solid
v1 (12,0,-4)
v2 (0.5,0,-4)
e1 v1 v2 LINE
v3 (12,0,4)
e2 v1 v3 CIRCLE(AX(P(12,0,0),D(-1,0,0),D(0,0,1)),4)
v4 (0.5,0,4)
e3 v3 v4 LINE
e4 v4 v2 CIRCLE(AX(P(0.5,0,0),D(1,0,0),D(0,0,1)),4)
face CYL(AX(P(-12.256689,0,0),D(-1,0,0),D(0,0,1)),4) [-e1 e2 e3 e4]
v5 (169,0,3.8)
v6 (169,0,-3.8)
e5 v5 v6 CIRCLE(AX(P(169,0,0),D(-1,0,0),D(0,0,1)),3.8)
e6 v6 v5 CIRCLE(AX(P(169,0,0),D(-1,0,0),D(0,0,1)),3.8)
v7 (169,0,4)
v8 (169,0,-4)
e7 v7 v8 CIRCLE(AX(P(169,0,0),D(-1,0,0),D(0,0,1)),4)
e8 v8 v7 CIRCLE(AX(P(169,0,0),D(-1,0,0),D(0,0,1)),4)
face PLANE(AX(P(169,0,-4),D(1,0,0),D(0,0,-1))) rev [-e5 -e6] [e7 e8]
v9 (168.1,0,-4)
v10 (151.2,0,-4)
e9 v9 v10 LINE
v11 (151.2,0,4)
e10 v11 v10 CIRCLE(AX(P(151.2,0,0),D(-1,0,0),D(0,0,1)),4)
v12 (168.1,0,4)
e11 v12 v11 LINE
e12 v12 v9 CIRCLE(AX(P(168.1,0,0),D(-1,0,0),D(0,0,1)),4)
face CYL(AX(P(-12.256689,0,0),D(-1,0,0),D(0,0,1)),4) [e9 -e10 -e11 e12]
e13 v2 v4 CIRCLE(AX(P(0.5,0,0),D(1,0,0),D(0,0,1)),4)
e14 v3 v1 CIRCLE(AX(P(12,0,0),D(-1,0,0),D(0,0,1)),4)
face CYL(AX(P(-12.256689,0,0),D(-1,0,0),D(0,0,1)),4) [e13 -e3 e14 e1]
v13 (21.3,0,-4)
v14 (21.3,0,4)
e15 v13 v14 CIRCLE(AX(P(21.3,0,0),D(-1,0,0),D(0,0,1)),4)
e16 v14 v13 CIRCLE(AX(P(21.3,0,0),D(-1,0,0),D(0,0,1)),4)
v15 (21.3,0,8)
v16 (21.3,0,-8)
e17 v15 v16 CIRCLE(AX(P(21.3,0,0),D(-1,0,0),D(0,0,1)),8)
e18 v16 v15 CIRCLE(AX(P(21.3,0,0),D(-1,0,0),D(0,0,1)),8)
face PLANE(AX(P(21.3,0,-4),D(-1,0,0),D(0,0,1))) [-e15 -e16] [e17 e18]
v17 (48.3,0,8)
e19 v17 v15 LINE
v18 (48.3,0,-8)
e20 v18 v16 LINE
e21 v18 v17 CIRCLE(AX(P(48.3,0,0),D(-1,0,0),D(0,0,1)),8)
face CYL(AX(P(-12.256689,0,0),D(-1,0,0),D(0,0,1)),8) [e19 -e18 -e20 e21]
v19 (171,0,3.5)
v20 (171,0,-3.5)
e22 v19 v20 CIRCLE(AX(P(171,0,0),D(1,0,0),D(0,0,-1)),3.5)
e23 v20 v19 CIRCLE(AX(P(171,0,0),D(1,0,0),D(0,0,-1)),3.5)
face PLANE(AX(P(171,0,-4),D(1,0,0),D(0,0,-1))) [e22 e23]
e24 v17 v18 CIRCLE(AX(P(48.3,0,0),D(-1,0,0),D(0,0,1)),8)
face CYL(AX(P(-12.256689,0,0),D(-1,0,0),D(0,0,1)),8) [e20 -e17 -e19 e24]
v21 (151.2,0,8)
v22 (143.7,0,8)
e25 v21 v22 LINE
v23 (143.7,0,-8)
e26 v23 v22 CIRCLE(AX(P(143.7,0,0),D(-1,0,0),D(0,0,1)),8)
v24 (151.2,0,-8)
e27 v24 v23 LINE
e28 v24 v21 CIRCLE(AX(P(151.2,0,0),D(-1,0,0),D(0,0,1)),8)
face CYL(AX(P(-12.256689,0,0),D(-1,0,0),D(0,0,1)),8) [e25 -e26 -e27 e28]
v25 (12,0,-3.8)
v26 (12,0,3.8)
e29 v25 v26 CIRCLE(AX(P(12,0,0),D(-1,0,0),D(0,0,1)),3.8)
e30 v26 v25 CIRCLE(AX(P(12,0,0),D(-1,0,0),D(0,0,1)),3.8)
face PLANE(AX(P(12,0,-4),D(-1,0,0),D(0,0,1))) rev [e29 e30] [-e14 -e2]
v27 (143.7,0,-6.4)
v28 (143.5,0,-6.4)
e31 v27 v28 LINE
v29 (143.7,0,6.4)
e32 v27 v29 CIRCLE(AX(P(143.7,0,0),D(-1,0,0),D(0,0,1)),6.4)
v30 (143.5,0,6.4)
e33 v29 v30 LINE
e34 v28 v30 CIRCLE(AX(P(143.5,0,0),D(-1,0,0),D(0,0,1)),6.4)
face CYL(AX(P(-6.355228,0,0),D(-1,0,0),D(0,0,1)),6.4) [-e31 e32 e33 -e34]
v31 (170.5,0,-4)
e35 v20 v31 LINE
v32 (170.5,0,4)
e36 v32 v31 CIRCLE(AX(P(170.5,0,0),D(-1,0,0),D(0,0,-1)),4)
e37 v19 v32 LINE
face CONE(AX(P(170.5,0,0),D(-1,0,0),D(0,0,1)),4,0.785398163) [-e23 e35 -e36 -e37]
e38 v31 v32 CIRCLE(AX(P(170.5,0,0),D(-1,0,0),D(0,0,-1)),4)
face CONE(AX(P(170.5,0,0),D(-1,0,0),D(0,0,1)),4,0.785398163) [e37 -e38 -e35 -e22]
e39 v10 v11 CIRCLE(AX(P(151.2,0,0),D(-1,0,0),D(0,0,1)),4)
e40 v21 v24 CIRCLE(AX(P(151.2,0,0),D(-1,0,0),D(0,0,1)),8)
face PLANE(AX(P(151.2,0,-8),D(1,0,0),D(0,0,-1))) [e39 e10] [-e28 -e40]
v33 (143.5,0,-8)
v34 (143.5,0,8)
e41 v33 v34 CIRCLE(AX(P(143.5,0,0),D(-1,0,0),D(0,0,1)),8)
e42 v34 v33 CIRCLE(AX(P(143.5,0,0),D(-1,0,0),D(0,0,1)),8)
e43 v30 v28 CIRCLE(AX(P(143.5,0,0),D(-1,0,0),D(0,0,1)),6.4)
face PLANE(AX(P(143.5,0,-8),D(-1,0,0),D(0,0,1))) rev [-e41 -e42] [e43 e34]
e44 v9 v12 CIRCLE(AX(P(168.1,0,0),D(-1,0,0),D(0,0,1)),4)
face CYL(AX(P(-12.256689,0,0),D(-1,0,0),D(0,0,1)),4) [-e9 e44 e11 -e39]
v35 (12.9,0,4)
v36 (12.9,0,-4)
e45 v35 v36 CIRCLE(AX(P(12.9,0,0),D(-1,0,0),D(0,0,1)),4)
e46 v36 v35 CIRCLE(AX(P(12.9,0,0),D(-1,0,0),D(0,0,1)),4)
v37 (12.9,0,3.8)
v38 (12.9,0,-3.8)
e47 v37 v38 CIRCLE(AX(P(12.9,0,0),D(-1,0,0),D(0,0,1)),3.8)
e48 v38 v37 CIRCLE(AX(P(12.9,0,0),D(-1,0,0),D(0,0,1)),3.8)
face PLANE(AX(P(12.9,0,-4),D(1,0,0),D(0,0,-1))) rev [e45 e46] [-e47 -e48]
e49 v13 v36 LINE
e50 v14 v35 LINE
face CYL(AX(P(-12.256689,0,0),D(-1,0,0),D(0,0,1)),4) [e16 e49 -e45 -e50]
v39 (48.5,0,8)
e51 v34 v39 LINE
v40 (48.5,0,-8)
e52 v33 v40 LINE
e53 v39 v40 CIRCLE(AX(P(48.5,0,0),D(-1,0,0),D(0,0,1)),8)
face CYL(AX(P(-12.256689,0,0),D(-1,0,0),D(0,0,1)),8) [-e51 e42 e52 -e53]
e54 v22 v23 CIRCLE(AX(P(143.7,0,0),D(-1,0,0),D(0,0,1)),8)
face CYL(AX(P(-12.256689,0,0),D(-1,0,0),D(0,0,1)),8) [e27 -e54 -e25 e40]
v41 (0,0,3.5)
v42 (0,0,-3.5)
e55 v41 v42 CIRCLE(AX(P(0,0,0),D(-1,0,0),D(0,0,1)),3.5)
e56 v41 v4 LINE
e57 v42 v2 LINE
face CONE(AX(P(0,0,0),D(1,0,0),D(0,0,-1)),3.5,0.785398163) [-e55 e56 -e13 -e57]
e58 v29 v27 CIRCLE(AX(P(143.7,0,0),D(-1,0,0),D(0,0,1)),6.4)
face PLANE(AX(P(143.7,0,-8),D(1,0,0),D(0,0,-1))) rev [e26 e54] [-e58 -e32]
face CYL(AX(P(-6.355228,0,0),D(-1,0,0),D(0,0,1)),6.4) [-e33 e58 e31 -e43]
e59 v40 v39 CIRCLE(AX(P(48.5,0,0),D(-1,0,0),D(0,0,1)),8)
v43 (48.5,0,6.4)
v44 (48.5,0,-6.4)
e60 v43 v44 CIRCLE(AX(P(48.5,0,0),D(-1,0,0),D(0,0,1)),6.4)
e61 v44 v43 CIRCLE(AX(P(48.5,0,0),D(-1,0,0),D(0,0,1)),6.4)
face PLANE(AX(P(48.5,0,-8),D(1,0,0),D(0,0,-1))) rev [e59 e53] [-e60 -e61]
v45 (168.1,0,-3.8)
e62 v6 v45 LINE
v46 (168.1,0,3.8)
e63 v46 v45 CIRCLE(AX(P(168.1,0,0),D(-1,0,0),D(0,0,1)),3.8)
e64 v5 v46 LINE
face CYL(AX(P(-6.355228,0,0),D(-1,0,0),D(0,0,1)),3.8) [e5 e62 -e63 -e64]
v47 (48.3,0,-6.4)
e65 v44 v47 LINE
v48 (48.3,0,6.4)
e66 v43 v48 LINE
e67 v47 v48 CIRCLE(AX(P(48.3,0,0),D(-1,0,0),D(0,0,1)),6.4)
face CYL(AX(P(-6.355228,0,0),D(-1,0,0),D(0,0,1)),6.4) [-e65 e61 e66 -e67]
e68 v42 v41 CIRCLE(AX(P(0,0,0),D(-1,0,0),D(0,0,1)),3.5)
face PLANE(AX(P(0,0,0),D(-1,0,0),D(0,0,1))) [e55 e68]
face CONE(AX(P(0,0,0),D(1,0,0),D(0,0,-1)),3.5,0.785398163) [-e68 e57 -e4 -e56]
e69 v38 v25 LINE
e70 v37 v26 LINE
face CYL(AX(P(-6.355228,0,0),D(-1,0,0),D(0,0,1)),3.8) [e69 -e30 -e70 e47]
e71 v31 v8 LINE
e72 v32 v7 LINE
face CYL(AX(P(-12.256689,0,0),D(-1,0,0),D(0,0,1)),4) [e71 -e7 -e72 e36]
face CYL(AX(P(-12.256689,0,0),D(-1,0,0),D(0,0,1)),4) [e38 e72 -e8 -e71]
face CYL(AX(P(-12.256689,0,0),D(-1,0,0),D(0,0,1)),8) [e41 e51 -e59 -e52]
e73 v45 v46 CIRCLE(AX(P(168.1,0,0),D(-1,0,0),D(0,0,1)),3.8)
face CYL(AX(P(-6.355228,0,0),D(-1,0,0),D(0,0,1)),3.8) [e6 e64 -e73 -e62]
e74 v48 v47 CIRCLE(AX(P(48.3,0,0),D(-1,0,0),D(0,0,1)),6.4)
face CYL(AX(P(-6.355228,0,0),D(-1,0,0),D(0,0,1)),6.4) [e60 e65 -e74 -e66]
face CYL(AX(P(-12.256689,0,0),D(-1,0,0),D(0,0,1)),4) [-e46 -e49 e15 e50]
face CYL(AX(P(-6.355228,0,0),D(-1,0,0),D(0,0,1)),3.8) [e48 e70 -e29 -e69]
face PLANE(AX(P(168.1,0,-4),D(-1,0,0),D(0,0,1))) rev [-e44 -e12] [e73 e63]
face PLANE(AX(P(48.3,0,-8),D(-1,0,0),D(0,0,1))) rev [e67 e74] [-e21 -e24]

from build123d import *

# Parameters (mm, degrees)
SKETCH2_W     = 0.2
SKETCH2_H     = 1.6
SKETCH2_W_2   = 0.9
SKETCH2_H_2   = 0.2
CHAMFER1_SIZE = 0.5


with BuildPart() as part:
    # Sketch1 → Revolve1 (revolve)
    with BuildSketch(Plane(origin=(0, 0, 0), x_dir=(1, 0, 0), z_dir=(0, 1, 0))):
        Polygon((0, 0), (0, -4), (21.3, -4), (21.3, -8), (151.2, -8), (151.2, -4), (171, -4), (171, 0), align=None)
    revolve(axis=Axis((-12.256689328, 0, 0), (1, 0, 0)))

    # Sketch2 → Cut-Revolve1 (revolve, cut)
    with BuildSketch(Plane(origin=(0, 0, 0), x_dir=(1, 0, 0), z_dir=(0, 1, 0))):
        with Locations((48.4, -7.2)):
            Rectangle(SKETCH2_W, SKETCH2_H)
        with Locations((143.6, -7.2)):
            Rectangle(SKETCH2_W, SKETCH2_H)
        with Locations((168.55, -3.9)):
            Rectangle(SKETCH2_W_2, SKETCH2_H_2)
        with Locations((12.45, -3.9)):
            Rectangle(SKETCH2_W_2, SKETCH2_H_2)
    revolve(axis=Axis((-6.355227553, 0, 0), (1, 0, 0)), mode=Mode.SUBTRACT)

    # Chamfer1
    chamfer1_edges = [part.edges().sort_by_distance(p)[0] for p in [
        (171, 0, -4),
        (0, 0, -4),
    ]]
    chamfer(chamfer1_edges, length=CHAMFER1_SIZE)


solid = part.part
